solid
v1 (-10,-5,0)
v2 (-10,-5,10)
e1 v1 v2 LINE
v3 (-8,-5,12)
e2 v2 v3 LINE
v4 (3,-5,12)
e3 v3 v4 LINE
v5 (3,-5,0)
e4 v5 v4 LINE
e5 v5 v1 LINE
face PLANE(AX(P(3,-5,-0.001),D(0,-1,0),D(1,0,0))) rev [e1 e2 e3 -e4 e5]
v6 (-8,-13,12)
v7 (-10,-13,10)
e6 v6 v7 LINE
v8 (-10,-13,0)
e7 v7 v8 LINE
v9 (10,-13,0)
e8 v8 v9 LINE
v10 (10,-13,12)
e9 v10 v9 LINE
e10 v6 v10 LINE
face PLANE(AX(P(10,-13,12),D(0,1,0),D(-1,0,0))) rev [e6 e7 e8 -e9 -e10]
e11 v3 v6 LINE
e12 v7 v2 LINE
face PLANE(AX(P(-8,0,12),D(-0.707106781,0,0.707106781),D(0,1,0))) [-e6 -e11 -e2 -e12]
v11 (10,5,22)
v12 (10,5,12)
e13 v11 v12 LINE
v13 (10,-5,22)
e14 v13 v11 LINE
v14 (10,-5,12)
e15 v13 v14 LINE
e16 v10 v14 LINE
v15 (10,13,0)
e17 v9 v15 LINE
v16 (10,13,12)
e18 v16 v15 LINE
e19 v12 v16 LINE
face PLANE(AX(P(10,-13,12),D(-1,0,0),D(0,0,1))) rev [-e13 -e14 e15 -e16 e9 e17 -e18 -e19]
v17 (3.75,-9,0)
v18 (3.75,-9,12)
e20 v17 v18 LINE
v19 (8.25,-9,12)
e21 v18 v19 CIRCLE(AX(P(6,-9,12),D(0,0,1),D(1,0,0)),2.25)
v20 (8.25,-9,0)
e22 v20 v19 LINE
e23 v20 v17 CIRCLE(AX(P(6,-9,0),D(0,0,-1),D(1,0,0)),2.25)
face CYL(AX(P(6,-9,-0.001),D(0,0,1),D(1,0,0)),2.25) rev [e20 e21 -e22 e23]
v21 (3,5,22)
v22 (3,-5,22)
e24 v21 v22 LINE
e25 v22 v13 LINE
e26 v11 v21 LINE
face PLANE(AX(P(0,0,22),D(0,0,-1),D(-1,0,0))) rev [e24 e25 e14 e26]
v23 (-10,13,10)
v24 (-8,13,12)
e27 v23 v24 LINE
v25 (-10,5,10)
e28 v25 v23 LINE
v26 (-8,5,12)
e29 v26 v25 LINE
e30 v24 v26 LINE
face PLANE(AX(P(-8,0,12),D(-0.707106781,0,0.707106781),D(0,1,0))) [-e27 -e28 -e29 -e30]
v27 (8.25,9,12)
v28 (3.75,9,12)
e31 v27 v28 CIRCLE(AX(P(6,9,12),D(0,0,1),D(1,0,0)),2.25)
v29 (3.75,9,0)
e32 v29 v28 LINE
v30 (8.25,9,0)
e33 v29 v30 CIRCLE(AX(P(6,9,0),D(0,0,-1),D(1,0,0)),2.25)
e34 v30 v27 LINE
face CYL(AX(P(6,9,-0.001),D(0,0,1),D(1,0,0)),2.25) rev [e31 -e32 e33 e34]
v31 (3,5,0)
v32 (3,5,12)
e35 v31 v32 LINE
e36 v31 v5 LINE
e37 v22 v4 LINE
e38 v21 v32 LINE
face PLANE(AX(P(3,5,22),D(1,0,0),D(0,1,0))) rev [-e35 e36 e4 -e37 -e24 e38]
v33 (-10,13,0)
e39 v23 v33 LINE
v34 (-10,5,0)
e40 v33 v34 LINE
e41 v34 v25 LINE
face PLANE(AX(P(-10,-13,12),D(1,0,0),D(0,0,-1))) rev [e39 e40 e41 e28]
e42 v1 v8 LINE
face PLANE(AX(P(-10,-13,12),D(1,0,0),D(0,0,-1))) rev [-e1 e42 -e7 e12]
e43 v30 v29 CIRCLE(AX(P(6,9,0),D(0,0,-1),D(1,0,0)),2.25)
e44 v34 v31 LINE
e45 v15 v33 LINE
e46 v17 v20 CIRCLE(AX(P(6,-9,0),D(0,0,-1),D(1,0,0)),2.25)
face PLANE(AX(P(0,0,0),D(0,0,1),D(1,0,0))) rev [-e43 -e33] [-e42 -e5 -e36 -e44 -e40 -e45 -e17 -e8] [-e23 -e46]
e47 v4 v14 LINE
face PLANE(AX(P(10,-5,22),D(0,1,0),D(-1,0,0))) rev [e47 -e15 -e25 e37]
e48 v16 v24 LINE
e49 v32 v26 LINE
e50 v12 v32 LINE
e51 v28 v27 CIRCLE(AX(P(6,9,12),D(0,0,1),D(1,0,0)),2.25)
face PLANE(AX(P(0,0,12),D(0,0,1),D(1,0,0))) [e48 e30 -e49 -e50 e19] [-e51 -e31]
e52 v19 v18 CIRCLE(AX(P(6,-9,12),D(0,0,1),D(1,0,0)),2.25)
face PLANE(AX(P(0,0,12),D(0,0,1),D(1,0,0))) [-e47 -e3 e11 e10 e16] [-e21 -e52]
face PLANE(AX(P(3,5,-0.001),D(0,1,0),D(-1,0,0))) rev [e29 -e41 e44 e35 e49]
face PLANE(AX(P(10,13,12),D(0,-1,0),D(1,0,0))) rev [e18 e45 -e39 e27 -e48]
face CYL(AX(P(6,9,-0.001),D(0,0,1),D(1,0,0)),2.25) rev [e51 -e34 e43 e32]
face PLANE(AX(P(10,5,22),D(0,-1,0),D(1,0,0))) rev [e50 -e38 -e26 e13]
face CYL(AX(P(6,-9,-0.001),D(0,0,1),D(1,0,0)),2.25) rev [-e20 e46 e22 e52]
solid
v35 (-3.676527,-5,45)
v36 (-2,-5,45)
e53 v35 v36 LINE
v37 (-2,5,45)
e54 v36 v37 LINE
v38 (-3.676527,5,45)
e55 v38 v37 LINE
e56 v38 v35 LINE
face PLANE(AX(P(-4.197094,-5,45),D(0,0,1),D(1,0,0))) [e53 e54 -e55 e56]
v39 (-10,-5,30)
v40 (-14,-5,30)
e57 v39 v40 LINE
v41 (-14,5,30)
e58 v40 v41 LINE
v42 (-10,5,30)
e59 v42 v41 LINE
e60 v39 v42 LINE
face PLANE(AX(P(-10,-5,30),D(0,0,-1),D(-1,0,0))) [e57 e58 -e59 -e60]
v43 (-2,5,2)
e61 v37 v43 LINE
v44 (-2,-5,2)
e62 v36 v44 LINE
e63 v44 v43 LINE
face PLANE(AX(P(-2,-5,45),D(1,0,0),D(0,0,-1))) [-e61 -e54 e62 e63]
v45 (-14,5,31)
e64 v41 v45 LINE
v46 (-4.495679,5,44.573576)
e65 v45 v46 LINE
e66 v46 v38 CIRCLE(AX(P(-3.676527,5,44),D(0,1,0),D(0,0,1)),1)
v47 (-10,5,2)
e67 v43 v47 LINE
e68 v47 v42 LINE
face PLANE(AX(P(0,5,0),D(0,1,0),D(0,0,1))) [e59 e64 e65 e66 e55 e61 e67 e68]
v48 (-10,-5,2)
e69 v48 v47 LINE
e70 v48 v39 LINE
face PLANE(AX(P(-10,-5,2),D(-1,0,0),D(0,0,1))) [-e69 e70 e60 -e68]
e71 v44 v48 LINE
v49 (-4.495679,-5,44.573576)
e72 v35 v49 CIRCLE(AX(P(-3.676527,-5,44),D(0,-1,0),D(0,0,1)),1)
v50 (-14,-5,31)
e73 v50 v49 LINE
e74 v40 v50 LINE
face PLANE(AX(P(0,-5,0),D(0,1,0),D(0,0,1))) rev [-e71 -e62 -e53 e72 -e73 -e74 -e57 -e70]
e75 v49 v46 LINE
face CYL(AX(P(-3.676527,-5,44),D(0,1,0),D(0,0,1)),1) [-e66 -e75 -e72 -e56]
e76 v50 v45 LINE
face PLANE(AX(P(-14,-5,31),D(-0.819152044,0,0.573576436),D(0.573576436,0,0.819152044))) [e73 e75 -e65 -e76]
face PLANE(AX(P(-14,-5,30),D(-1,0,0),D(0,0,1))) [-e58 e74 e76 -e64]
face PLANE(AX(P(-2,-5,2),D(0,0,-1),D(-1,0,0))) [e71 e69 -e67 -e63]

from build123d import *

# Parameters (mm, degrees)
SKETCH1_W                = 20
SKETCH1_H                = 26
BOSS_EXTRUDE1_DEPTH      = 12
CUT_EXTRUDE1_REACH       = 22.322
SKETCH2_R                = 2.25
SKETCH3_W                = 7
SKETCH3_H                = 10
BOSS_EXTRUDE2_DEPTH      = 10
CUT_EXTRUDE2_REACH       = 22.322
SKETCH4_W                = 13
SKETCH4_H                = 10
BOSS_EXTRUDE3_DEPTH      = 5
BOSS_EXTRUDE3_DEPTH_BACK = 5
CHAMFER1_SIZE            = 2
FILLET1_R                = 1


with BuildPart() as part:
    # Sketch1 → Boss-Extrude1 (new body)
    with BuildSketch(Plane.XY):
        Rectangle(SKETCH1_W, SKETCH1_H)
    extrude(amount=BOSS_EXTRUDE1_DEPTH)

    # Sketch2 → Cut-Extrude1 (cut, up to next)
    with BuildSketch(Plane.XY.offset(12), mode=Mode.PRIVATE) as cut_extrude1_sk1:
        with Locations((6, 9)):
            Circle(SKETCH2_R)
    cut_extrude1_tool1 = extrude(cut_extrude1_sk1.sketch, amount=-CUT_EXTRUDE1_REACH, mode=Mode.PRIVATE) & part.part
    # Sketch2 → Cut-Extrude1 (cut, up to next)
    with BuildSketch(Plane.XY.offset(12), mode=Mode.PRIVATE) as cut_extrude1_sk2:
        with Locations((6, -9)):
            Circle(SKETCH2_R)
    cut_extrude1_tool2 = extrude(cut_extrude1_sk2.sketch, amount=-CUT_EXTRUDE1_REACH, mode=Mode.PRIVATE) & part.part
    add(cut_extrude1_tool1.solids().sort_by_distance((6, 9, 12))[0], mode=Mode.SUBTRACT)
    add(cut_extrude1_tool2.solids().sort_by_distance((6, -9, 12))[0], mode=Mode.SUBTRACT)

    # Sketch3 → Boss-Extrude2 (add)
    with BuildSketch(Plane.XY.offset(12)):
        with Locations((6.5, 0)):
            Rectangle(SKETCH3_W, SKETCH3_H)
    extrude(amount=BOSS_EXTRUDE2_DEPTH)

    # Sketch4 → Cut-Extrude2 (cut, up to next)
    with BuildSketch(Plane.XY.offset(12), mode=Mode.PRIVATE) as cut_extrude2_sk1:
        with Locations((-3.5, 0)):
            Rectangle(SKETCH4_W, SKETCH4_H)
    cut_extrude2_tool1 = extrude(cut_extrude2_sk1.sketch, amount=-CUT_EXTRUDE2_REACH, mode=Mode.PRIVATE) & part.part
    add(cut_extrude2_tool1.solids().sort_by_distance((-3.5, 0, 12))[0], mode=Mode.SUBTRACT)

    # Chamfer1
    chamfer1_edges = [part.edges().sort_by_distance(p)[0] for p in [
        (-10, -9, 12),
        (-10, 9, 12),
    ]]
    chamfer(chamfer1_edges, length=CHAMFER1_SIZE)


with BuildPart() as body_2:
    # Sketch5 → Boss-Extrude3 (new, two sides: drawn at the far end of the back side and taken through both)
    with BuildSketch(Plane(origin=(0, 0, 0), x_dir=(1, 0, 0), z_dir=(0, 1, 0)).offset(-BOSS_EXTRUDE3_DEPTH_BACK)):
        Polygon((-10, -2), (-10, -30), (-14, -30), (-14, -31), (-4.197094465, -45), (-2, -45), (-2, -2), align=None)
    extrude(amount=BOSS_EXTRUDE3_DEPTH + BOSS_EXTRUDE3_DEPTH_BACK)

    # Fillet1
    fillet1_edges = [body_2.edges().sort_by_distance(p)[0] for p in [
        (-4.197094465, 0, 45),
    ]]
    fillet(fillet1_edges, radius=FILLET1_R)


solid = Compound([part.part, body_2.part])
